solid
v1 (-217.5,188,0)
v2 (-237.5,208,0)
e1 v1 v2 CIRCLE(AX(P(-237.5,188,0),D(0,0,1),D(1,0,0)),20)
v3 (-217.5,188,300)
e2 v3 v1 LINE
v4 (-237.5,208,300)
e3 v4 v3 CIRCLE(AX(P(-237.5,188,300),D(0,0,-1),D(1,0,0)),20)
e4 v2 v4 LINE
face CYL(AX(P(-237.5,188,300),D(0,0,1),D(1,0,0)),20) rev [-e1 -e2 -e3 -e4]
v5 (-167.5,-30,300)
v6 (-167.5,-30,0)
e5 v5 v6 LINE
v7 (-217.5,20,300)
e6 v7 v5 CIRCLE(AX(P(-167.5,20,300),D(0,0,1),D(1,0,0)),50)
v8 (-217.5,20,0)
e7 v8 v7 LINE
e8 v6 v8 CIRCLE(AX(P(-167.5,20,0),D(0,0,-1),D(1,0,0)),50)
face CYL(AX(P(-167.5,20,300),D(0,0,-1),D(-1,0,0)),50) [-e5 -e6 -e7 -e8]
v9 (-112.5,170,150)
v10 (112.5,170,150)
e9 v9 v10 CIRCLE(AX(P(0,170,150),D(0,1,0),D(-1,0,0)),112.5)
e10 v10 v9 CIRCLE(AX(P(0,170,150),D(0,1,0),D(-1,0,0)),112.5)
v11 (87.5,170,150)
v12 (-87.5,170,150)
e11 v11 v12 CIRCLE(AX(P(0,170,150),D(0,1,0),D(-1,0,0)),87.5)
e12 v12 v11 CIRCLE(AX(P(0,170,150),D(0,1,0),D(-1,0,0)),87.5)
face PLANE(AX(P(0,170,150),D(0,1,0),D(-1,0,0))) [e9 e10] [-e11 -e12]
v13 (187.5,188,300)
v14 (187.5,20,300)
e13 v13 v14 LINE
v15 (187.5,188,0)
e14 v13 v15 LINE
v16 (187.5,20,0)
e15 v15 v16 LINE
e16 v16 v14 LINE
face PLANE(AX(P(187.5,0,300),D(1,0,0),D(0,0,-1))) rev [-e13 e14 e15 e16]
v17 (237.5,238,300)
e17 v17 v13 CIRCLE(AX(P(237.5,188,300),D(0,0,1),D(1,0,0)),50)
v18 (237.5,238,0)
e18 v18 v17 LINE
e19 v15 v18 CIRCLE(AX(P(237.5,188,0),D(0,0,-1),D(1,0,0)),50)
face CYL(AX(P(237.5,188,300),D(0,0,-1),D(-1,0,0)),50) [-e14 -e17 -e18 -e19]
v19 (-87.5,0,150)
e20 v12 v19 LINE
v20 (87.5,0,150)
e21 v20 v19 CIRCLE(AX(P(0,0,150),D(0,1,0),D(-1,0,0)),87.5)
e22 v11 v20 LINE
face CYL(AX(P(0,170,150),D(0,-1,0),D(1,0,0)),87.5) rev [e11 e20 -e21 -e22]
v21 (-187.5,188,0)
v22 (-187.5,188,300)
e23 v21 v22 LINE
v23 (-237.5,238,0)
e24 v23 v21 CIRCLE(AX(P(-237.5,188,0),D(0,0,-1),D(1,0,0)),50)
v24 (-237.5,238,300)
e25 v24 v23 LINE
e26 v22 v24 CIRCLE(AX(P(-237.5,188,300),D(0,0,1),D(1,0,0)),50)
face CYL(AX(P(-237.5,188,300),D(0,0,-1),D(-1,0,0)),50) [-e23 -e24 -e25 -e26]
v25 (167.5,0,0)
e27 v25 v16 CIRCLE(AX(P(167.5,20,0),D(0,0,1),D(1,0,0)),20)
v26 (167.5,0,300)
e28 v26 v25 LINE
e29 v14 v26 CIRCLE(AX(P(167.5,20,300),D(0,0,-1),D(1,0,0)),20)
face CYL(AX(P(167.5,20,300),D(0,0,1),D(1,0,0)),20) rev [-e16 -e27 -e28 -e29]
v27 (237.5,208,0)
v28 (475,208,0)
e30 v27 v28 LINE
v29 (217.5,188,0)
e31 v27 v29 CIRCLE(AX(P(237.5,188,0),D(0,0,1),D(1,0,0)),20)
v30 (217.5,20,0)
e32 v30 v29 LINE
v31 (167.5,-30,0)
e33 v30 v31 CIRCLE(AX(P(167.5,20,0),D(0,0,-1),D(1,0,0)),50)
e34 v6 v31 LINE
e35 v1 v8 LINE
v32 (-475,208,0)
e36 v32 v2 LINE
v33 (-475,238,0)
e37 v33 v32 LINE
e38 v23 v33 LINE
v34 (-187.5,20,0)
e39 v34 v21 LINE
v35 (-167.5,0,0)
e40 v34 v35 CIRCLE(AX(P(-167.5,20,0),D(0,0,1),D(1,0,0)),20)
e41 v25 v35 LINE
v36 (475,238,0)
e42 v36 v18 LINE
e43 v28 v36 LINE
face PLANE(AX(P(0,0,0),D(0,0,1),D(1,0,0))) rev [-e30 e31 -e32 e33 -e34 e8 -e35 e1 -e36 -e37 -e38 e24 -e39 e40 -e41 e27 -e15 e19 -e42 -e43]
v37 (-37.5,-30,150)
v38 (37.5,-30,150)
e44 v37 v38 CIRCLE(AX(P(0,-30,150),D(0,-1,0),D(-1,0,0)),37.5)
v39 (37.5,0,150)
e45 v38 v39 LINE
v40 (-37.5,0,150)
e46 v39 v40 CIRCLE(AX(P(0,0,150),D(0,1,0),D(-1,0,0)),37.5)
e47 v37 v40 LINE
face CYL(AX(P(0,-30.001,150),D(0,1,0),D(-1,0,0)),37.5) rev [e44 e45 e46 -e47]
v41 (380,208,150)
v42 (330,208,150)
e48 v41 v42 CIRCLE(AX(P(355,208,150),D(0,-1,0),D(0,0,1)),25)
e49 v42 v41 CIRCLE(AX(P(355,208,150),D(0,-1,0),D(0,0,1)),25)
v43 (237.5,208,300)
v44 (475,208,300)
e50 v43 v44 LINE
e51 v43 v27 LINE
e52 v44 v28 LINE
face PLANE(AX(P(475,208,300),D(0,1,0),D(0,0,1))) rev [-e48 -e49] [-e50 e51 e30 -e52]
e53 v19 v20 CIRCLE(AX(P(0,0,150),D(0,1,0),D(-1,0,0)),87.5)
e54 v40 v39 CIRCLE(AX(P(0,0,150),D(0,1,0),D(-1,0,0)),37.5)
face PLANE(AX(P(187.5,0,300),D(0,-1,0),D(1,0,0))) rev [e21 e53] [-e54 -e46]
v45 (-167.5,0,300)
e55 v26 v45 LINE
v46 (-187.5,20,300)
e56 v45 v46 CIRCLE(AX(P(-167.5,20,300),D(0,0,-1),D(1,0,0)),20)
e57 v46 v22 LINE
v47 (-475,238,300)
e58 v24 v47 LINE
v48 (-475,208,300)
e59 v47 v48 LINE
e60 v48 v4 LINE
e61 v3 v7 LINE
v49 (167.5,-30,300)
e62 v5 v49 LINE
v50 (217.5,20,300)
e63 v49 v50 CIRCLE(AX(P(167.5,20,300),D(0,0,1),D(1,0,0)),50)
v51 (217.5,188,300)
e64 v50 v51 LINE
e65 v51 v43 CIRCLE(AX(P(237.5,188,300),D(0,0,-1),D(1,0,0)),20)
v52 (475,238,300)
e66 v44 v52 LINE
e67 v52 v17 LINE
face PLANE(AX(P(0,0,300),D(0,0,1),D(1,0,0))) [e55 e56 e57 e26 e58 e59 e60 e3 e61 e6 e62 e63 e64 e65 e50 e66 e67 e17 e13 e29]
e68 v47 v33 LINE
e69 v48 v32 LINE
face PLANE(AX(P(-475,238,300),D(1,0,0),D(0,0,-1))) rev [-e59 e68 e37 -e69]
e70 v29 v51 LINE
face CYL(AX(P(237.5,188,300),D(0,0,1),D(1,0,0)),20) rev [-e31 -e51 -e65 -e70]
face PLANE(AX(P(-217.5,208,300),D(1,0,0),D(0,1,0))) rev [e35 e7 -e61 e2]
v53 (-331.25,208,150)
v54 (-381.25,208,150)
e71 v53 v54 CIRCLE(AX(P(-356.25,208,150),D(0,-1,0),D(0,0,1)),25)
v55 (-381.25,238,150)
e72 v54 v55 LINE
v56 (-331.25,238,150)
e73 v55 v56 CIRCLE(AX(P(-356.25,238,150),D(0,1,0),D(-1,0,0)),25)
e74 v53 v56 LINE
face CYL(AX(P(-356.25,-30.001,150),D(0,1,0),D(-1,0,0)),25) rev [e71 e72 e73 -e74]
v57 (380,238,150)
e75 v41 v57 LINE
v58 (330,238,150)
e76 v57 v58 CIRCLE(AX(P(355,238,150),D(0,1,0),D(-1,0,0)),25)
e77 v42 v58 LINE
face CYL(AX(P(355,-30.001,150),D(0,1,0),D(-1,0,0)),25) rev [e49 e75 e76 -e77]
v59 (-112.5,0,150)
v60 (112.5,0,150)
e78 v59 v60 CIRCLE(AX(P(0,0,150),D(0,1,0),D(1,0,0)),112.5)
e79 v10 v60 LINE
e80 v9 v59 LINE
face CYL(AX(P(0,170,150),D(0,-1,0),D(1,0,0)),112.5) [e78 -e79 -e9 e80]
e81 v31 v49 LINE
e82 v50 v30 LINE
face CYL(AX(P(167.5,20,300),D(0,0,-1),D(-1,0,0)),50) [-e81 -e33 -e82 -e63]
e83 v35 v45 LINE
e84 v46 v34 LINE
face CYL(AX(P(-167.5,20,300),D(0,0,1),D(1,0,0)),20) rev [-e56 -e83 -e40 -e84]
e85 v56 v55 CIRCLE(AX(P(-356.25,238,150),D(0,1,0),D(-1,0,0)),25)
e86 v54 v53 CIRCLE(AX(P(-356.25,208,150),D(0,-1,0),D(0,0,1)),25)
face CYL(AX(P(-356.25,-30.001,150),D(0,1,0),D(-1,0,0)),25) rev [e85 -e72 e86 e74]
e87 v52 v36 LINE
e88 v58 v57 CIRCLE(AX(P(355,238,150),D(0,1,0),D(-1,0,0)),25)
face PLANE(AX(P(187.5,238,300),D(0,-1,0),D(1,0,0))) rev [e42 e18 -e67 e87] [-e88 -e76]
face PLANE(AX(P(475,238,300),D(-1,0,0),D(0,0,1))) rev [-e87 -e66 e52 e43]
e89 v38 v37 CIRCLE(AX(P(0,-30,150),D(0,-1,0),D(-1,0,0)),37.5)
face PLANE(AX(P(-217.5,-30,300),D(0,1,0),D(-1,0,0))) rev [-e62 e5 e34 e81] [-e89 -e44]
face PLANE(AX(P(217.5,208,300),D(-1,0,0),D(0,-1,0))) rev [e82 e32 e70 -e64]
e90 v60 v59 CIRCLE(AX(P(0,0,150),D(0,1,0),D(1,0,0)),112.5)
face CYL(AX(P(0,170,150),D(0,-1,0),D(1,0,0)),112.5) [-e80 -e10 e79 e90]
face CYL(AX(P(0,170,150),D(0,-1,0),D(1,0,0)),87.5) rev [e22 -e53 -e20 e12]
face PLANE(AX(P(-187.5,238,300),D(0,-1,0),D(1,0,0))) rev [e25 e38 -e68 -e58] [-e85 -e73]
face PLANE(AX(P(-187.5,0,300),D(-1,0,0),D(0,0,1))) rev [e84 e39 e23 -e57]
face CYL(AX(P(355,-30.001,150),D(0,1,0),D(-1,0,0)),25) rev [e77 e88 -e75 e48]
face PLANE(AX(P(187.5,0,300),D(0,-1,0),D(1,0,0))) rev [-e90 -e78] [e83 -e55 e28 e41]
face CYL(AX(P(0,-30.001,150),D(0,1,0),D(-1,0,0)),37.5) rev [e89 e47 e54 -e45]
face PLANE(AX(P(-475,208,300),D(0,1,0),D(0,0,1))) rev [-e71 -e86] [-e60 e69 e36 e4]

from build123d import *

# Parameters (mm, degrees)
BOSS_EXTRUDE2_DEPTH = 300
FILLET3_R           = 20
FILLET4_R           = 50
FILLET5_R           = 20
SKETCH2_R           = 112.5
SKETCH2_R_2         = 87.5
BOSS_EXTRUDE3_DEPTH = 170
CUT_EXTRUDE1_REACH  = 612.139
SKETCH3_R           = 37.5
CUT_EXTRUDE2_REACH  = 624.454
SKETCH4_R           = 25


with BuildPart() as part:
    # Sketch1 → Boss-Extrude2 (new body)
    with BuildSketch(Plane.XY):
        Polygon((187.5, 0), (-187.5, 0), (-187.5, 238), (-475, 238), (-475, 208), (-217.5, 208), (-217.5, -30), (217.5, -30), (217.5, 208), (475, 208), (475, 238), (187.5, 238), align=None)
    extrude(amount=BOSS_EXTRUDE2_DEPTH)

    # Fillet3
    fillet3_edges = [part.edges().sort_by_distance(p)[0] for p in [
        (-187.5, 0, 150),
        (187.5, 0, 150),
    ]]
    fillet(fillet3_edges, radius=FILLET3_R)

    # Fillet4
    fillet4_edges = [part.edges().sort_by_distance(p)[0] for p in [
        (187.5, 238, 150),
        (217.5, -30, 150),
        (-217.5, -30, 150),
        (-187.5, 238, 150),
    ]]
    fillet(fillet4_edges, radius=FILLET4_R)

    # Fillet5
    fillet5_edges = [part.edges().sort_by_distance(p)[0] for p in [
        (217.5, 208, 150),
        (-217.5, 208, 150),
    ]]
    fillet(fillet5_edges, radius=FILLET5_R)

    # Sketch2 → Boss-Extrude3 (add)
    with BuildSketch(Plane(origin=(0, 0, 0), x_dir=(1, 0, 0), z_dir=(0, 1, 0))):
        with Locations((0, -150)):
            Circle(SKETCH2_R)
        with Locations(Location((0, -150, 0), (0, 0, 180))):
            Circle(SKETCH2_R_2, mode=Mode.SUBTRACT)
    extrude(amount=BOSS_EXTRUDE3_DEPTH)

    # Sketch3 → Cut-Extrude1 (cut, up to next)
    with BuildSketch(Plane(origin=(0, 0, 0), x_dir=(1, 0, 0), z_dir=(0, 1, 0)), mode=Mode.PRIVATE) as cut_extrude1_sk1:
        with Locations(Location((0, -150, 0), (0, 0, 180))):
            Circle(SKETCH3_R)
    cut_extrude1_tool1 = extrude(cut_extrude1_sk1.sketch, amount=-CUT_EXTRUDE1_REACH, mode=Mode.PRIVATE) & part.part
    add(cut_extrude1_tool1.solids().sort_by_distance((0, 0, 150))[0], mode=Mode.SUBTRACT)

    # Sketch4 → Cut-Extrude2 (cut, up to next)
    with BuildSketch(Plane(origin=(0, 238, 0), x_dir=(1, 0, 0), z_dir=(0, 1, 0)), mode=Mode.PRIVATE) as cut_extrude2_sk1:
        with Locations(Location((-356.25, -150, 0), (0, 0, 180))):
            Circle(SKETCH4_R)
    cut_extrude2_tool1 = extrude(cut_extrude2_sk1.sketch, amount=-CUT_EXTRUDE2_REACH, mode=Mode.PRIVATE) & part.part
    # Sketch4 → Cut-Extrude2 (cut, up to next)
    with BuildSketch(Plane(origin=(0, 238, 0), x_dir=(1, 0, 0), z_dir=(0, 1, 0)), mode=Mode.PRIVATE) as cut_extrude2_sk2:
        with Locations(Location((355, -150, 0), (0, 0, 180))):
            Circle(SKETCH4_R)
    cut_extrude2_tool2 = extrude(cut_extrude2_sk2.sketch, amount=-CUT_EXTRUDE2_REACH, mode=Mode.PRIVATE) & part.part
    add(cut_extrude2_tool1.solids().sort_by_distance((-356.25, 238, 150))[0], mode=Mode.SUBTRACT)
    add(cut_extrude2_tool2.solids().sort_by_distance((355, 238, 150))[0], mode=Mode.SUBTRACT)


solid = part.part
